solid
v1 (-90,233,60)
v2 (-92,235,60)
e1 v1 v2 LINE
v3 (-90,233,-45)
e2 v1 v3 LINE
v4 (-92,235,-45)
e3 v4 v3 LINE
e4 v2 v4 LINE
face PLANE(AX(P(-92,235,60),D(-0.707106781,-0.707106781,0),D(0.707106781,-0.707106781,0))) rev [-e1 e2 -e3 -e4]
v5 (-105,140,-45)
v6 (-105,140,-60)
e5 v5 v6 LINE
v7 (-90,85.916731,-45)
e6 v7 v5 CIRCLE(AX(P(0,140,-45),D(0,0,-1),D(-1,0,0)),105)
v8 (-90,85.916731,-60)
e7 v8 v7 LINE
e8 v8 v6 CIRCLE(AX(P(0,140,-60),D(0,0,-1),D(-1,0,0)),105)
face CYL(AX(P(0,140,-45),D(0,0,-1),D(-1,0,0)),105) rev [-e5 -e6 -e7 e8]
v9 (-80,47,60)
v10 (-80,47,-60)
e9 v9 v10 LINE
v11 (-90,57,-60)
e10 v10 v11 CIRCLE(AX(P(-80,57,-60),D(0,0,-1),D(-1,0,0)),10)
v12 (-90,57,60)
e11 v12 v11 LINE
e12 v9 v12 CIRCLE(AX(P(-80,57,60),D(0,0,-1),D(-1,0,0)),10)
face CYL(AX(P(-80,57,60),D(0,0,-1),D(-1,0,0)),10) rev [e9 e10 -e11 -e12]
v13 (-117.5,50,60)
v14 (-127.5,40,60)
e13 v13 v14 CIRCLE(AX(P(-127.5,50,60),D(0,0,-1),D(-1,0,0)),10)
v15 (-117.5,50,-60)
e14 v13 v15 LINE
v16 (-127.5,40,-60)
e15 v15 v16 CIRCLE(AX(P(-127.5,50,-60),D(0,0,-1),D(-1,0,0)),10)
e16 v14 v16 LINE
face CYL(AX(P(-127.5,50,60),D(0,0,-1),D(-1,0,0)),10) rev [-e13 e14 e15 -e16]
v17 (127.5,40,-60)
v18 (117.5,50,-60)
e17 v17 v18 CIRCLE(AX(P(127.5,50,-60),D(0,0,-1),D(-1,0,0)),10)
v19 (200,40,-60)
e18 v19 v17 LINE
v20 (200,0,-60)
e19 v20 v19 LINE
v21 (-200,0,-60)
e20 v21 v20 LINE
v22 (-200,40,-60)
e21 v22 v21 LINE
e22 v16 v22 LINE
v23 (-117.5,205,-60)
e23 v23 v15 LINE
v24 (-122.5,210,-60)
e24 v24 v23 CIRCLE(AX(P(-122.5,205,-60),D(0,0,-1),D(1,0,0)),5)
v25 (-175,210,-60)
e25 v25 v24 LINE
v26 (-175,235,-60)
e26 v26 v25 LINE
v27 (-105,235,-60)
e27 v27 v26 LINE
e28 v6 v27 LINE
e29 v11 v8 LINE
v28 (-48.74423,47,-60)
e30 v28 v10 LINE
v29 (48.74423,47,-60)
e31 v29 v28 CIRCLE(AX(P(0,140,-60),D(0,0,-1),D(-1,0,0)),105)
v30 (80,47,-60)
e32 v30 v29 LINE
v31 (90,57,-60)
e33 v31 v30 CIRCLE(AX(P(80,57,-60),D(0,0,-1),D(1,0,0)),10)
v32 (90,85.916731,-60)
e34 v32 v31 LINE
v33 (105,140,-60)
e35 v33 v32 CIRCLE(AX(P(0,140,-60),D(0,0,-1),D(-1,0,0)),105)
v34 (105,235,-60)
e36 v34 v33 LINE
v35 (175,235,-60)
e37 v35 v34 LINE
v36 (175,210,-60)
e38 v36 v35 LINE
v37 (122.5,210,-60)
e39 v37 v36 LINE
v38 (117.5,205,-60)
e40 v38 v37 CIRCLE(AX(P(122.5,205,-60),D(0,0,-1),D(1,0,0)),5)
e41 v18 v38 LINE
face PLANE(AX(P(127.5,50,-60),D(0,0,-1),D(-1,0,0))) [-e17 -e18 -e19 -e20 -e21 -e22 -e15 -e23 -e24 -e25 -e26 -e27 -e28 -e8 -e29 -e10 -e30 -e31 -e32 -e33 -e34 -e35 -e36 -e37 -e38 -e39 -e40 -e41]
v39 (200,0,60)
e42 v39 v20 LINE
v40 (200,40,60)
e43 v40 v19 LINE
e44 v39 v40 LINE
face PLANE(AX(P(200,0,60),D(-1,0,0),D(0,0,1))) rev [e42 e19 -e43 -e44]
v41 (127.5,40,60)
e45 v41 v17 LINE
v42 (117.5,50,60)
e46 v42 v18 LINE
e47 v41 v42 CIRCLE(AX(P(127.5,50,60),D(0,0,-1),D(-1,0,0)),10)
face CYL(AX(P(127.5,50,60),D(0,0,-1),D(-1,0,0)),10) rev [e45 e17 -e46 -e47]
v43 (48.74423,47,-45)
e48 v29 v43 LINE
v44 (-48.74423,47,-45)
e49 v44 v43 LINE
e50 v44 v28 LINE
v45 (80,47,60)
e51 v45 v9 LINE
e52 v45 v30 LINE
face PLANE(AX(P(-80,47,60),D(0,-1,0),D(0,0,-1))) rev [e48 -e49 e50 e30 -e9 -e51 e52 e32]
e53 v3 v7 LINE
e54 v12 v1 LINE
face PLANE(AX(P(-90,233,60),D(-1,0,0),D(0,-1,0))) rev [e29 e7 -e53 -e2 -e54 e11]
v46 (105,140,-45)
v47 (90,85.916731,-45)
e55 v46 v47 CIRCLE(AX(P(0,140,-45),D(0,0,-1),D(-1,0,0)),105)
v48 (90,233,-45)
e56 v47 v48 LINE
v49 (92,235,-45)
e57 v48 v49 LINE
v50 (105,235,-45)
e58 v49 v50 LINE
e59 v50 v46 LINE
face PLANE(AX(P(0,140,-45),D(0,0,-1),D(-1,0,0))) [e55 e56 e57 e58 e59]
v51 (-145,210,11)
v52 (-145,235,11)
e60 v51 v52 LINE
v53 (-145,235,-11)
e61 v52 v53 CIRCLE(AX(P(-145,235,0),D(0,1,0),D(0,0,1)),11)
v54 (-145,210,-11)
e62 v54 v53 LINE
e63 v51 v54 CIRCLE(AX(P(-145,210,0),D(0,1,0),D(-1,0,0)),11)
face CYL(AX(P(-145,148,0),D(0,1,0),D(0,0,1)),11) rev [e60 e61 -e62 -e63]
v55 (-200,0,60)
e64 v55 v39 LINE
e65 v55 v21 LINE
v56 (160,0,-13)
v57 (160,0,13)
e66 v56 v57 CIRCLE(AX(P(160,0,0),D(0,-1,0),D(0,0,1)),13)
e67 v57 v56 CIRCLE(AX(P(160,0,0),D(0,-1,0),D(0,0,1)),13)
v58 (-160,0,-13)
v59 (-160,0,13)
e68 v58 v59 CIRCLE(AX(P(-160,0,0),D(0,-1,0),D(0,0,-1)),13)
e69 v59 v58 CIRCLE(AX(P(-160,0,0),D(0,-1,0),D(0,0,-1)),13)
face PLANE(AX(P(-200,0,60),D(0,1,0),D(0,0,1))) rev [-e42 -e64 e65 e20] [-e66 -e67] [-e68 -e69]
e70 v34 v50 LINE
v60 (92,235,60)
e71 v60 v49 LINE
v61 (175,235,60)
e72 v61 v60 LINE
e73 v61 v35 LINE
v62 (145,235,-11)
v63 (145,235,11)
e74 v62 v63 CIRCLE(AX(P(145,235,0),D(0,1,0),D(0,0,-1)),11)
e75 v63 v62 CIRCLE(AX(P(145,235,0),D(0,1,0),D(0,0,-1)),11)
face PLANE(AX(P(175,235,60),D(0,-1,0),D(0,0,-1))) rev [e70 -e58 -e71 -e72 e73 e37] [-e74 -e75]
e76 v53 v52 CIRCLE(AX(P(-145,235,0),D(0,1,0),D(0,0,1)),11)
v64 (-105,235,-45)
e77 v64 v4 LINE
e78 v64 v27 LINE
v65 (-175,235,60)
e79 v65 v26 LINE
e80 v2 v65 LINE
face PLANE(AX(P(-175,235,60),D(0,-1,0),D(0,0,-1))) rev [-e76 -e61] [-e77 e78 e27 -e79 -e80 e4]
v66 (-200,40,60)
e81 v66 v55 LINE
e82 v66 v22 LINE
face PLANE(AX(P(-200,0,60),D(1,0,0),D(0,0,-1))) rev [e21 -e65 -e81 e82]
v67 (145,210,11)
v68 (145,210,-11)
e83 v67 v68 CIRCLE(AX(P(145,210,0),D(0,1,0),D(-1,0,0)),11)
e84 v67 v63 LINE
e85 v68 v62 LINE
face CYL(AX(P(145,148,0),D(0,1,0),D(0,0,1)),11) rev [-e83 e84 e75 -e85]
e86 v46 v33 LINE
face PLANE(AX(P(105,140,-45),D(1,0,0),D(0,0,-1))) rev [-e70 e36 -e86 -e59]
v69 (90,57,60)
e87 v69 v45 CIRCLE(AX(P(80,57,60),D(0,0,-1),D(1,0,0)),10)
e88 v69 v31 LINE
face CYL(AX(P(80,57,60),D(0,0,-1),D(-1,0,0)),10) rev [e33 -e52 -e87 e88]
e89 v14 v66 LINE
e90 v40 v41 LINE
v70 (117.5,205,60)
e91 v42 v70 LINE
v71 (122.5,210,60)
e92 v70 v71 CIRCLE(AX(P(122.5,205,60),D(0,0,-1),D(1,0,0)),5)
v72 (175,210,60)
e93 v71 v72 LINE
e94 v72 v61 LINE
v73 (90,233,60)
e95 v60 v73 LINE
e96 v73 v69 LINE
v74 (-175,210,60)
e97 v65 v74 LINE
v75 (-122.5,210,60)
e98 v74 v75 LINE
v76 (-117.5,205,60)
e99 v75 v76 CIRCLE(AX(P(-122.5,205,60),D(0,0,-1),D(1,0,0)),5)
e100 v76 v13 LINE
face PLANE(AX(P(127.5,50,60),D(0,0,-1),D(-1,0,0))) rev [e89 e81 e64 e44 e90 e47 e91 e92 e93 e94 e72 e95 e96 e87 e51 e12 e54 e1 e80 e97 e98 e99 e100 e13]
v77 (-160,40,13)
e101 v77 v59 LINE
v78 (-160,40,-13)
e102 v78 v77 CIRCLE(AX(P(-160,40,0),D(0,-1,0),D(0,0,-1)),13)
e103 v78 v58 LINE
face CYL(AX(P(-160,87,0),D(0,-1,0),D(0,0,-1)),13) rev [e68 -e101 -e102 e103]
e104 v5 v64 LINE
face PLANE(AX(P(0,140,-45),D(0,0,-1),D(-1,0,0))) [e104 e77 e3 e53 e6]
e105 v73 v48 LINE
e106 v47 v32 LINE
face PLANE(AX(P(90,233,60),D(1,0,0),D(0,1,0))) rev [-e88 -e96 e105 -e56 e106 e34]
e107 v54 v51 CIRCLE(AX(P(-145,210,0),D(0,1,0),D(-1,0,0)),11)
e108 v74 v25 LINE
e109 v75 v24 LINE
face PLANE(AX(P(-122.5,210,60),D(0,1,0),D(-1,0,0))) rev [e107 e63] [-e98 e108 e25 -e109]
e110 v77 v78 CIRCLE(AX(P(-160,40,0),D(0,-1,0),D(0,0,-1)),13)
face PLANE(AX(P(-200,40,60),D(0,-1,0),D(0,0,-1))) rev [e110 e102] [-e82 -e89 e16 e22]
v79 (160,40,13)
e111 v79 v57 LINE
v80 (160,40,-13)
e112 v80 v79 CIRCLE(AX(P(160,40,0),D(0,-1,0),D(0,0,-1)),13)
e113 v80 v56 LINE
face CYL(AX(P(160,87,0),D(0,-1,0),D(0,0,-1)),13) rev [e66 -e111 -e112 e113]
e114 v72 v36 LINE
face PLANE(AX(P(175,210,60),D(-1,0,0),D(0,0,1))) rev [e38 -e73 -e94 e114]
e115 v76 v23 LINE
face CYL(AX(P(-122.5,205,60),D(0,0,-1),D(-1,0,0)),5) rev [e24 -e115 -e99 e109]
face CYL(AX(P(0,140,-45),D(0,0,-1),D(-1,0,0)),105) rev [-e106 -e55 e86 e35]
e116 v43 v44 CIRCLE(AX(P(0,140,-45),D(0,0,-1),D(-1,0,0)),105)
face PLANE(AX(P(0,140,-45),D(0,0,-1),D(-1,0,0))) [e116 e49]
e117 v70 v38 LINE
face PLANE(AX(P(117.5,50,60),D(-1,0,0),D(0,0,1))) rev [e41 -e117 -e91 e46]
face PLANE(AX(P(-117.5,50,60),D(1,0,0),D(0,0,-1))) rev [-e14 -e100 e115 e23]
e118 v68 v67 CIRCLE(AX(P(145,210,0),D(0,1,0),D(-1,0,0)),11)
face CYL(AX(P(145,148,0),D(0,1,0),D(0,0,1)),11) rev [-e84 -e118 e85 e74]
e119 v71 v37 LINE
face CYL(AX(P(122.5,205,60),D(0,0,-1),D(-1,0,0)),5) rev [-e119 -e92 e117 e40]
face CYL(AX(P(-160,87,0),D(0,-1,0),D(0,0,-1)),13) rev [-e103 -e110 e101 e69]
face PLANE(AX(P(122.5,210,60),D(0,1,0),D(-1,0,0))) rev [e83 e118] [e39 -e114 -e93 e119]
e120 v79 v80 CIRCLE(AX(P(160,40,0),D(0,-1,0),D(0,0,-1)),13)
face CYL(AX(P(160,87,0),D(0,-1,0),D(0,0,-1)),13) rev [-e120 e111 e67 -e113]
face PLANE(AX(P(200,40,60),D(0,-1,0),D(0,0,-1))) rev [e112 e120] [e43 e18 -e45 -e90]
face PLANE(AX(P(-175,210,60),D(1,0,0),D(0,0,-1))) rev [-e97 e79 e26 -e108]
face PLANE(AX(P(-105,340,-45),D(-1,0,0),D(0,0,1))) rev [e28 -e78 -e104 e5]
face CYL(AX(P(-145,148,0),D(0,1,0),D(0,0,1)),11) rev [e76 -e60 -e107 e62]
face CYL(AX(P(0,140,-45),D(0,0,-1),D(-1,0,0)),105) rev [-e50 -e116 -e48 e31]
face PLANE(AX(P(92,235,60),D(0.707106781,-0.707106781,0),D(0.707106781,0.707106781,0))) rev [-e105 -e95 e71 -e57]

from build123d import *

# Parameters (mm, degrees)
BOSS_EXTRUDE1_DEPTH = 60
SKETCH2_R           = 13
CUT_EXTRUDE1_DEPTH  = 87
SKETCH3_R           = 11
CUT_EXTRUDE2_DEPTH  = 87
CUT_EXTRUDE3_DEPTH  = 15


with BuildPart() as part:
    # Sketch1 → Boss-Extrude1 (new, symmetric)
    with BuildSketch(Plane.XY):
        with BuildLine():
            Line((-200, 0), (200, 0))
            Line((200, 0), (200, 40))
            Line((200, 40), (127.5, 40))
            ThreePointArc((127.5, 40), (120.428932188, 42.928932188), (117.5, 50))
            Line((117.5, 50), (117.5, 205))
            ThreePointArc((117.5, 205), (118.964466094, 208.535533906), (122.5, 210))
            Line((122.5, 210), (175, 210))
            Line((175, 210), (175, 235))
            Line((175, 235), (92, 235))
            Line((92, 235), (90, 233))
            Line((90, 233), (90, 57))
            ThreePointArc((90, 57), (87.071067812, 49.928932188), (80, 47))
            Line((80, 47), (-80, 47))
            ThreePointArc((-80, 47), (-87.071067812, 49.928932188), (-90, 57))
            Line((-90, 57), (-90, 233))
            Line((-90, 233), (-92, 235))
            Line((-92, 235), (-175, 235))
            Line((-175, 235), (-175, 210))
            Line((-175, 210), (-122.5, 210))
            ThreePointArc((-122.5, 210), (-118.964466094, 208.535533906), (-117.5, 205))
            Line((-117.5, 205), (-117.5, 50))
            ThreePointArc((-117.5, 50), (-120.428932188, 42.928932188), (-127.5, 40))
            Line((-127.5, 40), (-200, 40))
            Line((-200, 40), (-200, 0))
        make_face()
    extrude(amount=BOSS_EXTRUDE1_DEPTH, both=True)

    # Sketch2 → Cut-Extrude1 (cut)
    with BuildSketch(Plane.XZ):
        with Locations(Location((-160, 0, 0), (0, 0, 270))):
            Circle(SKETCH2_R)
        with Locations(Location((160, 0, 0), (0, 0, 270))):
            Circle(SKETCH2_R)
    extrude(amount=-CUT_EXTRUDE1_DEPTH, mode=Mode.SUBTRACT)

    # Sketch3 → Cut-Extrude2 (cut)
    with BuildSketch(Plane(origin=(0, 235, 0), x_dir=(1, 0, 0), z_dir=(0, 1, 0))):
        with Locations(Location((-145, 0, 0), (0, 0, 270))):
            Circle(SKETCH3_R)
        with Locations(Location((145, 0, 0), (0, 0, 180))):
            Circle(SKETCH3_R)
    extrude(amount=-CUT_EXTRUDE2_DEPTH, mode=Mode.SUBTRACT)

    # Sketch4 → Cut-Extrude3 (cut)
    with BuildSketch(Plane(origin=(0, 0, -60), x_dir=(-1, 0, 0), z_dir=(0, 0, -1))):
        with BuildLine():
            Line((-105, 140), (-105, 340))
            Line((-105, 340), (105, 340))
            Line((105, 340), (105, 140))
            ThreePointArc((105, 140), (0, 35), (-105, 140))
        make_face()
    extrude(amount=-CUT_EXTRUDE3_DEPTH, mode=Mode.SUBTRACT)


solid = part.part
